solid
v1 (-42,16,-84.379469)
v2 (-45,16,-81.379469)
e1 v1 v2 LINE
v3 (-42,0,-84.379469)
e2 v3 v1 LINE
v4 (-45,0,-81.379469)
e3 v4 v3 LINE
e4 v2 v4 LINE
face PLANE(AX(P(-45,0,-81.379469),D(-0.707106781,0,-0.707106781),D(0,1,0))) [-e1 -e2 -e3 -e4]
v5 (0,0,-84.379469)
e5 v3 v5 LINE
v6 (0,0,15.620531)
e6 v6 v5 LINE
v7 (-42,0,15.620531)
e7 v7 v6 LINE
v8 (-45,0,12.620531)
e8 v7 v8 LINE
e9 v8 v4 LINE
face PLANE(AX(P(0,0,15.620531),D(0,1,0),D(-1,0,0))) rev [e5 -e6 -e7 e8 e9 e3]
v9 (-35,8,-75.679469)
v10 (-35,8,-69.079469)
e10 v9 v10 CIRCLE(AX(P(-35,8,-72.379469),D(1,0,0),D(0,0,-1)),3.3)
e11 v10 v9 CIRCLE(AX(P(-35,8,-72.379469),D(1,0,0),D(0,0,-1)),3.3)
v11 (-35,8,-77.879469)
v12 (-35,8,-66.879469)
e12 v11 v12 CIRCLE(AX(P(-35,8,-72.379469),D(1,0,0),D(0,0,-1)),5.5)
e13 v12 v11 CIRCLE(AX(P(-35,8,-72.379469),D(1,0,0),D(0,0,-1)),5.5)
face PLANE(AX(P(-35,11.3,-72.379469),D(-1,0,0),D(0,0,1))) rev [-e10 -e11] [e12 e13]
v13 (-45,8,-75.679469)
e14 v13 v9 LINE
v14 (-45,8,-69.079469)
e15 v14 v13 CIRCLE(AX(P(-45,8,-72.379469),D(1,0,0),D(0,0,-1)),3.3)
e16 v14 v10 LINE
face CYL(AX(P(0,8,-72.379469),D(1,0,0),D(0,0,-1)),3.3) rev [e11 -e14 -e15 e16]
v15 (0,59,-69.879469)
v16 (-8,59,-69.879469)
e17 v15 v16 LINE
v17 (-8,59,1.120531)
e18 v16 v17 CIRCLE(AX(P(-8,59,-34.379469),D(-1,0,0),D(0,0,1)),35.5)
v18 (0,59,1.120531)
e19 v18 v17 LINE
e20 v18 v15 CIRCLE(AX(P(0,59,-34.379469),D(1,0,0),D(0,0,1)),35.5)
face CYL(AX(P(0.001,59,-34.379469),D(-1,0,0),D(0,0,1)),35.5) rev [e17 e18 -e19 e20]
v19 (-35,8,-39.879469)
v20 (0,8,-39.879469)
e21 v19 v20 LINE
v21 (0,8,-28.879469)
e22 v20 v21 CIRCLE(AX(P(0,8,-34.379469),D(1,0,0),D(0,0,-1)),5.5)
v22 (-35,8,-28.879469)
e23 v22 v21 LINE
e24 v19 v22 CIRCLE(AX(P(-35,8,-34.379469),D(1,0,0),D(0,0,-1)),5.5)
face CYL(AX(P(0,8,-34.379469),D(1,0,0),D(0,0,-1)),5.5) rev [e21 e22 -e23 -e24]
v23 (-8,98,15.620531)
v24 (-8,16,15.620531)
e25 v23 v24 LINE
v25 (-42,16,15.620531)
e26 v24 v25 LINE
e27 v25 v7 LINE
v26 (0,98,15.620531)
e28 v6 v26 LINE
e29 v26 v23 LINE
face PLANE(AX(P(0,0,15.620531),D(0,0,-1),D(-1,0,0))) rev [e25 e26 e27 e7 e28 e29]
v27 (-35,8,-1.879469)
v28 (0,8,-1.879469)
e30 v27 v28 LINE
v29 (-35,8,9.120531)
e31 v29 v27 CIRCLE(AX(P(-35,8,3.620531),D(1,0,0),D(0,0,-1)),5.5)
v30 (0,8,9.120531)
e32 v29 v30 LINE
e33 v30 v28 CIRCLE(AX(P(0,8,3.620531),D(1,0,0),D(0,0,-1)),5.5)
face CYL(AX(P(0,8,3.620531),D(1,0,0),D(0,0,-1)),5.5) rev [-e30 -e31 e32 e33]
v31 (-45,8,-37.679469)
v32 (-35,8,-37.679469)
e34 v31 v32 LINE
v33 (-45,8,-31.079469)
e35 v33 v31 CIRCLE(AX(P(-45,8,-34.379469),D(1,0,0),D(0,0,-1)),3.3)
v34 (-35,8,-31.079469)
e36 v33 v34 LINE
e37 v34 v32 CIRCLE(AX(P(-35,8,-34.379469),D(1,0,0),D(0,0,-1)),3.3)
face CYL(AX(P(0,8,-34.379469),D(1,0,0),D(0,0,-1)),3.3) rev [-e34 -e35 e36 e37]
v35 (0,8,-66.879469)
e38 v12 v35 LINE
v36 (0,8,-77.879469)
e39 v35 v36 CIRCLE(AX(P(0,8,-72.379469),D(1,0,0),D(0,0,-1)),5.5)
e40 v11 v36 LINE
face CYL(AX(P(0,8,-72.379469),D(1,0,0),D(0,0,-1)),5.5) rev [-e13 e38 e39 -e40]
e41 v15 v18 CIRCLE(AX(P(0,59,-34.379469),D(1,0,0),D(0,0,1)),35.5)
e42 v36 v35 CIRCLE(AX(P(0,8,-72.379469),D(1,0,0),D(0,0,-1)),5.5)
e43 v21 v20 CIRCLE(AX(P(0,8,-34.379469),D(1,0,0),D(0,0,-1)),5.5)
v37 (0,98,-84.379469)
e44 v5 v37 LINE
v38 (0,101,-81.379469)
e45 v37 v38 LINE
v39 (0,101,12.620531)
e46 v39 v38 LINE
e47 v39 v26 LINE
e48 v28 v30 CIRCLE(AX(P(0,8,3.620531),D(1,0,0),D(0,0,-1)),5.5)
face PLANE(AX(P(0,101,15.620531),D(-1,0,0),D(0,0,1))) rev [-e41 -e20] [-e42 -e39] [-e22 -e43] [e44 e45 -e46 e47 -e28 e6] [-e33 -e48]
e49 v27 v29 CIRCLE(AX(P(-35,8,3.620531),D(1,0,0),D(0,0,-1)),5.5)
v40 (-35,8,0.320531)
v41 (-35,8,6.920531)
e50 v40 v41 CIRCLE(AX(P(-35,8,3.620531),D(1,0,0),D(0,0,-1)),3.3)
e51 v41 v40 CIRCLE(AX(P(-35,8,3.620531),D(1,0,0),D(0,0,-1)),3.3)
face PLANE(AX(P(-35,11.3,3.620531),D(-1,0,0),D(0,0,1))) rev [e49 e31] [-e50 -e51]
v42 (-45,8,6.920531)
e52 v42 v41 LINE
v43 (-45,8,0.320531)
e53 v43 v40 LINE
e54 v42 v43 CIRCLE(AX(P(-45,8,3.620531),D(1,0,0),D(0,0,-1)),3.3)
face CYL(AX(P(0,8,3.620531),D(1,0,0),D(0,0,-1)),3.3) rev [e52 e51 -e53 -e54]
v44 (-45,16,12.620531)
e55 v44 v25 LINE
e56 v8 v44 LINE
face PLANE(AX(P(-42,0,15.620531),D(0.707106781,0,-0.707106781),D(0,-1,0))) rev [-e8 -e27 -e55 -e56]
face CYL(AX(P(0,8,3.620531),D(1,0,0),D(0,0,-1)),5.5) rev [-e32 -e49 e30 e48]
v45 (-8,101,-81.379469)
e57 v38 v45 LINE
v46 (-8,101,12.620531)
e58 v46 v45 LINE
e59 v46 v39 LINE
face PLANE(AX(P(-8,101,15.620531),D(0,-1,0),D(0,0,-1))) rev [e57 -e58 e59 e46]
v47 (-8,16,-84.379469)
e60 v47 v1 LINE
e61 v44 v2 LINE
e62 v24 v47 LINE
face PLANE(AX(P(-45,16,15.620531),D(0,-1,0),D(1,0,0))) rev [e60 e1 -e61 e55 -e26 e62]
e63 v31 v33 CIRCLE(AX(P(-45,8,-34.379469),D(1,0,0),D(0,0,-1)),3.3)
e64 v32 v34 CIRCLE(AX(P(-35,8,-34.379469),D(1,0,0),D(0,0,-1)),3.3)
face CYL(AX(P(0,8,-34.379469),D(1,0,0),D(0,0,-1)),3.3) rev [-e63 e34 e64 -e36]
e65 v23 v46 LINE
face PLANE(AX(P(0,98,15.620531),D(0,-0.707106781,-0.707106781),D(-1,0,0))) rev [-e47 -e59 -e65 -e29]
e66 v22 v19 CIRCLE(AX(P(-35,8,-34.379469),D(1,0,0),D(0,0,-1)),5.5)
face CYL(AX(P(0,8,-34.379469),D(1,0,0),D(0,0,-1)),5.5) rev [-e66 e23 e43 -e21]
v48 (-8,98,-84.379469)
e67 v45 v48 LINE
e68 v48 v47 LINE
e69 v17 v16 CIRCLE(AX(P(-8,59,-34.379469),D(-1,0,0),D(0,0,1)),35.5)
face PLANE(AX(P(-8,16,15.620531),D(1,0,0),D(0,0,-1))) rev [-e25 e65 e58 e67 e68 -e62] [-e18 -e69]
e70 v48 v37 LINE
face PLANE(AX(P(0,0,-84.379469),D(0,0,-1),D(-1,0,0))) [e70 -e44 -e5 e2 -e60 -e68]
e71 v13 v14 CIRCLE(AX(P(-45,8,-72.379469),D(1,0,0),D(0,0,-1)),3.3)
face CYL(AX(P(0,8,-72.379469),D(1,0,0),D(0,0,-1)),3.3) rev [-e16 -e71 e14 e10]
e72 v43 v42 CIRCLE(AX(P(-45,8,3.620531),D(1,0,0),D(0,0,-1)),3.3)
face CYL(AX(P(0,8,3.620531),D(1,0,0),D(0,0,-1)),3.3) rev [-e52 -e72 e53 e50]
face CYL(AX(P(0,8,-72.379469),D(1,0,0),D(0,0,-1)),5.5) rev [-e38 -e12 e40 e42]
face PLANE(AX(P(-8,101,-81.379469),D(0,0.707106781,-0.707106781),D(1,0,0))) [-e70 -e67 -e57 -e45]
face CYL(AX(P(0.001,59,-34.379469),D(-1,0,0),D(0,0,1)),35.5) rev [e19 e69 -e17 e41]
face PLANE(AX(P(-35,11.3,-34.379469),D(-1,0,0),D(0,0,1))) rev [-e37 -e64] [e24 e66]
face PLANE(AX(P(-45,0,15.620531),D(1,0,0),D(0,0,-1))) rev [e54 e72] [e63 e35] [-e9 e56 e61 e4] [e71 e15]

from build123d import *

# Parameters (mm, degrees)
EXTRUDE_1_DEPTH           = 50
CHAMFER_1_SIZE            = 3
CUT_EXTRUDE_1_REACH       = 138.711
SKETCH_3_R                = 35.5
HOLE_WIZARD_1_D           = 6.6
HOLE_WIZARD_1_CBORE_D     = 11
HOLE_WIZARD_1_CBORE_DEPTH = 35


with BuildPart() as part:
    # 草图2 → 凸台-拉伸1 (new, symmetric)
    with BuildSketch(Plane(origin=(409.637600706, 0.5, -34.379468655), x_dir=(1, 0, 0), z_dir=(0, 0, 1))):
        Polygon((-409.637600706, 100.5), (-409.637600706, -0.5), (-454.637600706, -0.5), (-454.637600706, 15.5), (-417.637600706, 15.5), (-417.637600706, 100.5), align=None)
    extrude(amount=EXTRUDE_1_DEPTH, both=True)

    # 倒角1
    chamfer_1_edges = [part.edges().sort_by_distance(p)[0] for p in [
        (-45, 8, 15.620531345),
        (-4, 101, 15.620531345),
        (-45, 8, -84.379468655),
        (-4, 101, -84.379468655),
    ]]
    chamfer(chamfer_1_edges, length=CHAMFER_1_SIZE)

    # 草图3 → 切除-拉伸1 (cut, up to next)
    with BuildSketch(Plane.ZY.offset(8), mode=Mode.PRIVATE) as cut_extrude_1_sk1:
        with Locations((-34.379468655, 59)):
            Circle(SKETCH_3_R)
    cut_extrude_1_tool1 = extrude(cut_extrude_1_sk1.sketch, amount=-CUT_EXTRUDE_1_REACH, mode=Mode.PRIVATE) & part.part
    add(cut_extrude_1_tool1.solids().sort_by_distance((-8, 59, -34.379469))[0], mode=Mode.SUBTRACT)

    # 打孔尺寸(%根据)内六角圆柱头螺钉的类型1 (through all)
    with Locations(Plane(origin=(0, 8, 3.620531345), x_dir=(0, 0, 1), z_dir=(1, 0, 0))):
        with Locations((0, 0), (-38, 0), (-76, 0)):
            CounterBoreHole(HOLE_WIZARD_1_D / 2, HOLE_WIZARD_1_CBORE_D / 2, HOLE_WIZARD_1_CBORE_DEPTH)


solid = part.part
